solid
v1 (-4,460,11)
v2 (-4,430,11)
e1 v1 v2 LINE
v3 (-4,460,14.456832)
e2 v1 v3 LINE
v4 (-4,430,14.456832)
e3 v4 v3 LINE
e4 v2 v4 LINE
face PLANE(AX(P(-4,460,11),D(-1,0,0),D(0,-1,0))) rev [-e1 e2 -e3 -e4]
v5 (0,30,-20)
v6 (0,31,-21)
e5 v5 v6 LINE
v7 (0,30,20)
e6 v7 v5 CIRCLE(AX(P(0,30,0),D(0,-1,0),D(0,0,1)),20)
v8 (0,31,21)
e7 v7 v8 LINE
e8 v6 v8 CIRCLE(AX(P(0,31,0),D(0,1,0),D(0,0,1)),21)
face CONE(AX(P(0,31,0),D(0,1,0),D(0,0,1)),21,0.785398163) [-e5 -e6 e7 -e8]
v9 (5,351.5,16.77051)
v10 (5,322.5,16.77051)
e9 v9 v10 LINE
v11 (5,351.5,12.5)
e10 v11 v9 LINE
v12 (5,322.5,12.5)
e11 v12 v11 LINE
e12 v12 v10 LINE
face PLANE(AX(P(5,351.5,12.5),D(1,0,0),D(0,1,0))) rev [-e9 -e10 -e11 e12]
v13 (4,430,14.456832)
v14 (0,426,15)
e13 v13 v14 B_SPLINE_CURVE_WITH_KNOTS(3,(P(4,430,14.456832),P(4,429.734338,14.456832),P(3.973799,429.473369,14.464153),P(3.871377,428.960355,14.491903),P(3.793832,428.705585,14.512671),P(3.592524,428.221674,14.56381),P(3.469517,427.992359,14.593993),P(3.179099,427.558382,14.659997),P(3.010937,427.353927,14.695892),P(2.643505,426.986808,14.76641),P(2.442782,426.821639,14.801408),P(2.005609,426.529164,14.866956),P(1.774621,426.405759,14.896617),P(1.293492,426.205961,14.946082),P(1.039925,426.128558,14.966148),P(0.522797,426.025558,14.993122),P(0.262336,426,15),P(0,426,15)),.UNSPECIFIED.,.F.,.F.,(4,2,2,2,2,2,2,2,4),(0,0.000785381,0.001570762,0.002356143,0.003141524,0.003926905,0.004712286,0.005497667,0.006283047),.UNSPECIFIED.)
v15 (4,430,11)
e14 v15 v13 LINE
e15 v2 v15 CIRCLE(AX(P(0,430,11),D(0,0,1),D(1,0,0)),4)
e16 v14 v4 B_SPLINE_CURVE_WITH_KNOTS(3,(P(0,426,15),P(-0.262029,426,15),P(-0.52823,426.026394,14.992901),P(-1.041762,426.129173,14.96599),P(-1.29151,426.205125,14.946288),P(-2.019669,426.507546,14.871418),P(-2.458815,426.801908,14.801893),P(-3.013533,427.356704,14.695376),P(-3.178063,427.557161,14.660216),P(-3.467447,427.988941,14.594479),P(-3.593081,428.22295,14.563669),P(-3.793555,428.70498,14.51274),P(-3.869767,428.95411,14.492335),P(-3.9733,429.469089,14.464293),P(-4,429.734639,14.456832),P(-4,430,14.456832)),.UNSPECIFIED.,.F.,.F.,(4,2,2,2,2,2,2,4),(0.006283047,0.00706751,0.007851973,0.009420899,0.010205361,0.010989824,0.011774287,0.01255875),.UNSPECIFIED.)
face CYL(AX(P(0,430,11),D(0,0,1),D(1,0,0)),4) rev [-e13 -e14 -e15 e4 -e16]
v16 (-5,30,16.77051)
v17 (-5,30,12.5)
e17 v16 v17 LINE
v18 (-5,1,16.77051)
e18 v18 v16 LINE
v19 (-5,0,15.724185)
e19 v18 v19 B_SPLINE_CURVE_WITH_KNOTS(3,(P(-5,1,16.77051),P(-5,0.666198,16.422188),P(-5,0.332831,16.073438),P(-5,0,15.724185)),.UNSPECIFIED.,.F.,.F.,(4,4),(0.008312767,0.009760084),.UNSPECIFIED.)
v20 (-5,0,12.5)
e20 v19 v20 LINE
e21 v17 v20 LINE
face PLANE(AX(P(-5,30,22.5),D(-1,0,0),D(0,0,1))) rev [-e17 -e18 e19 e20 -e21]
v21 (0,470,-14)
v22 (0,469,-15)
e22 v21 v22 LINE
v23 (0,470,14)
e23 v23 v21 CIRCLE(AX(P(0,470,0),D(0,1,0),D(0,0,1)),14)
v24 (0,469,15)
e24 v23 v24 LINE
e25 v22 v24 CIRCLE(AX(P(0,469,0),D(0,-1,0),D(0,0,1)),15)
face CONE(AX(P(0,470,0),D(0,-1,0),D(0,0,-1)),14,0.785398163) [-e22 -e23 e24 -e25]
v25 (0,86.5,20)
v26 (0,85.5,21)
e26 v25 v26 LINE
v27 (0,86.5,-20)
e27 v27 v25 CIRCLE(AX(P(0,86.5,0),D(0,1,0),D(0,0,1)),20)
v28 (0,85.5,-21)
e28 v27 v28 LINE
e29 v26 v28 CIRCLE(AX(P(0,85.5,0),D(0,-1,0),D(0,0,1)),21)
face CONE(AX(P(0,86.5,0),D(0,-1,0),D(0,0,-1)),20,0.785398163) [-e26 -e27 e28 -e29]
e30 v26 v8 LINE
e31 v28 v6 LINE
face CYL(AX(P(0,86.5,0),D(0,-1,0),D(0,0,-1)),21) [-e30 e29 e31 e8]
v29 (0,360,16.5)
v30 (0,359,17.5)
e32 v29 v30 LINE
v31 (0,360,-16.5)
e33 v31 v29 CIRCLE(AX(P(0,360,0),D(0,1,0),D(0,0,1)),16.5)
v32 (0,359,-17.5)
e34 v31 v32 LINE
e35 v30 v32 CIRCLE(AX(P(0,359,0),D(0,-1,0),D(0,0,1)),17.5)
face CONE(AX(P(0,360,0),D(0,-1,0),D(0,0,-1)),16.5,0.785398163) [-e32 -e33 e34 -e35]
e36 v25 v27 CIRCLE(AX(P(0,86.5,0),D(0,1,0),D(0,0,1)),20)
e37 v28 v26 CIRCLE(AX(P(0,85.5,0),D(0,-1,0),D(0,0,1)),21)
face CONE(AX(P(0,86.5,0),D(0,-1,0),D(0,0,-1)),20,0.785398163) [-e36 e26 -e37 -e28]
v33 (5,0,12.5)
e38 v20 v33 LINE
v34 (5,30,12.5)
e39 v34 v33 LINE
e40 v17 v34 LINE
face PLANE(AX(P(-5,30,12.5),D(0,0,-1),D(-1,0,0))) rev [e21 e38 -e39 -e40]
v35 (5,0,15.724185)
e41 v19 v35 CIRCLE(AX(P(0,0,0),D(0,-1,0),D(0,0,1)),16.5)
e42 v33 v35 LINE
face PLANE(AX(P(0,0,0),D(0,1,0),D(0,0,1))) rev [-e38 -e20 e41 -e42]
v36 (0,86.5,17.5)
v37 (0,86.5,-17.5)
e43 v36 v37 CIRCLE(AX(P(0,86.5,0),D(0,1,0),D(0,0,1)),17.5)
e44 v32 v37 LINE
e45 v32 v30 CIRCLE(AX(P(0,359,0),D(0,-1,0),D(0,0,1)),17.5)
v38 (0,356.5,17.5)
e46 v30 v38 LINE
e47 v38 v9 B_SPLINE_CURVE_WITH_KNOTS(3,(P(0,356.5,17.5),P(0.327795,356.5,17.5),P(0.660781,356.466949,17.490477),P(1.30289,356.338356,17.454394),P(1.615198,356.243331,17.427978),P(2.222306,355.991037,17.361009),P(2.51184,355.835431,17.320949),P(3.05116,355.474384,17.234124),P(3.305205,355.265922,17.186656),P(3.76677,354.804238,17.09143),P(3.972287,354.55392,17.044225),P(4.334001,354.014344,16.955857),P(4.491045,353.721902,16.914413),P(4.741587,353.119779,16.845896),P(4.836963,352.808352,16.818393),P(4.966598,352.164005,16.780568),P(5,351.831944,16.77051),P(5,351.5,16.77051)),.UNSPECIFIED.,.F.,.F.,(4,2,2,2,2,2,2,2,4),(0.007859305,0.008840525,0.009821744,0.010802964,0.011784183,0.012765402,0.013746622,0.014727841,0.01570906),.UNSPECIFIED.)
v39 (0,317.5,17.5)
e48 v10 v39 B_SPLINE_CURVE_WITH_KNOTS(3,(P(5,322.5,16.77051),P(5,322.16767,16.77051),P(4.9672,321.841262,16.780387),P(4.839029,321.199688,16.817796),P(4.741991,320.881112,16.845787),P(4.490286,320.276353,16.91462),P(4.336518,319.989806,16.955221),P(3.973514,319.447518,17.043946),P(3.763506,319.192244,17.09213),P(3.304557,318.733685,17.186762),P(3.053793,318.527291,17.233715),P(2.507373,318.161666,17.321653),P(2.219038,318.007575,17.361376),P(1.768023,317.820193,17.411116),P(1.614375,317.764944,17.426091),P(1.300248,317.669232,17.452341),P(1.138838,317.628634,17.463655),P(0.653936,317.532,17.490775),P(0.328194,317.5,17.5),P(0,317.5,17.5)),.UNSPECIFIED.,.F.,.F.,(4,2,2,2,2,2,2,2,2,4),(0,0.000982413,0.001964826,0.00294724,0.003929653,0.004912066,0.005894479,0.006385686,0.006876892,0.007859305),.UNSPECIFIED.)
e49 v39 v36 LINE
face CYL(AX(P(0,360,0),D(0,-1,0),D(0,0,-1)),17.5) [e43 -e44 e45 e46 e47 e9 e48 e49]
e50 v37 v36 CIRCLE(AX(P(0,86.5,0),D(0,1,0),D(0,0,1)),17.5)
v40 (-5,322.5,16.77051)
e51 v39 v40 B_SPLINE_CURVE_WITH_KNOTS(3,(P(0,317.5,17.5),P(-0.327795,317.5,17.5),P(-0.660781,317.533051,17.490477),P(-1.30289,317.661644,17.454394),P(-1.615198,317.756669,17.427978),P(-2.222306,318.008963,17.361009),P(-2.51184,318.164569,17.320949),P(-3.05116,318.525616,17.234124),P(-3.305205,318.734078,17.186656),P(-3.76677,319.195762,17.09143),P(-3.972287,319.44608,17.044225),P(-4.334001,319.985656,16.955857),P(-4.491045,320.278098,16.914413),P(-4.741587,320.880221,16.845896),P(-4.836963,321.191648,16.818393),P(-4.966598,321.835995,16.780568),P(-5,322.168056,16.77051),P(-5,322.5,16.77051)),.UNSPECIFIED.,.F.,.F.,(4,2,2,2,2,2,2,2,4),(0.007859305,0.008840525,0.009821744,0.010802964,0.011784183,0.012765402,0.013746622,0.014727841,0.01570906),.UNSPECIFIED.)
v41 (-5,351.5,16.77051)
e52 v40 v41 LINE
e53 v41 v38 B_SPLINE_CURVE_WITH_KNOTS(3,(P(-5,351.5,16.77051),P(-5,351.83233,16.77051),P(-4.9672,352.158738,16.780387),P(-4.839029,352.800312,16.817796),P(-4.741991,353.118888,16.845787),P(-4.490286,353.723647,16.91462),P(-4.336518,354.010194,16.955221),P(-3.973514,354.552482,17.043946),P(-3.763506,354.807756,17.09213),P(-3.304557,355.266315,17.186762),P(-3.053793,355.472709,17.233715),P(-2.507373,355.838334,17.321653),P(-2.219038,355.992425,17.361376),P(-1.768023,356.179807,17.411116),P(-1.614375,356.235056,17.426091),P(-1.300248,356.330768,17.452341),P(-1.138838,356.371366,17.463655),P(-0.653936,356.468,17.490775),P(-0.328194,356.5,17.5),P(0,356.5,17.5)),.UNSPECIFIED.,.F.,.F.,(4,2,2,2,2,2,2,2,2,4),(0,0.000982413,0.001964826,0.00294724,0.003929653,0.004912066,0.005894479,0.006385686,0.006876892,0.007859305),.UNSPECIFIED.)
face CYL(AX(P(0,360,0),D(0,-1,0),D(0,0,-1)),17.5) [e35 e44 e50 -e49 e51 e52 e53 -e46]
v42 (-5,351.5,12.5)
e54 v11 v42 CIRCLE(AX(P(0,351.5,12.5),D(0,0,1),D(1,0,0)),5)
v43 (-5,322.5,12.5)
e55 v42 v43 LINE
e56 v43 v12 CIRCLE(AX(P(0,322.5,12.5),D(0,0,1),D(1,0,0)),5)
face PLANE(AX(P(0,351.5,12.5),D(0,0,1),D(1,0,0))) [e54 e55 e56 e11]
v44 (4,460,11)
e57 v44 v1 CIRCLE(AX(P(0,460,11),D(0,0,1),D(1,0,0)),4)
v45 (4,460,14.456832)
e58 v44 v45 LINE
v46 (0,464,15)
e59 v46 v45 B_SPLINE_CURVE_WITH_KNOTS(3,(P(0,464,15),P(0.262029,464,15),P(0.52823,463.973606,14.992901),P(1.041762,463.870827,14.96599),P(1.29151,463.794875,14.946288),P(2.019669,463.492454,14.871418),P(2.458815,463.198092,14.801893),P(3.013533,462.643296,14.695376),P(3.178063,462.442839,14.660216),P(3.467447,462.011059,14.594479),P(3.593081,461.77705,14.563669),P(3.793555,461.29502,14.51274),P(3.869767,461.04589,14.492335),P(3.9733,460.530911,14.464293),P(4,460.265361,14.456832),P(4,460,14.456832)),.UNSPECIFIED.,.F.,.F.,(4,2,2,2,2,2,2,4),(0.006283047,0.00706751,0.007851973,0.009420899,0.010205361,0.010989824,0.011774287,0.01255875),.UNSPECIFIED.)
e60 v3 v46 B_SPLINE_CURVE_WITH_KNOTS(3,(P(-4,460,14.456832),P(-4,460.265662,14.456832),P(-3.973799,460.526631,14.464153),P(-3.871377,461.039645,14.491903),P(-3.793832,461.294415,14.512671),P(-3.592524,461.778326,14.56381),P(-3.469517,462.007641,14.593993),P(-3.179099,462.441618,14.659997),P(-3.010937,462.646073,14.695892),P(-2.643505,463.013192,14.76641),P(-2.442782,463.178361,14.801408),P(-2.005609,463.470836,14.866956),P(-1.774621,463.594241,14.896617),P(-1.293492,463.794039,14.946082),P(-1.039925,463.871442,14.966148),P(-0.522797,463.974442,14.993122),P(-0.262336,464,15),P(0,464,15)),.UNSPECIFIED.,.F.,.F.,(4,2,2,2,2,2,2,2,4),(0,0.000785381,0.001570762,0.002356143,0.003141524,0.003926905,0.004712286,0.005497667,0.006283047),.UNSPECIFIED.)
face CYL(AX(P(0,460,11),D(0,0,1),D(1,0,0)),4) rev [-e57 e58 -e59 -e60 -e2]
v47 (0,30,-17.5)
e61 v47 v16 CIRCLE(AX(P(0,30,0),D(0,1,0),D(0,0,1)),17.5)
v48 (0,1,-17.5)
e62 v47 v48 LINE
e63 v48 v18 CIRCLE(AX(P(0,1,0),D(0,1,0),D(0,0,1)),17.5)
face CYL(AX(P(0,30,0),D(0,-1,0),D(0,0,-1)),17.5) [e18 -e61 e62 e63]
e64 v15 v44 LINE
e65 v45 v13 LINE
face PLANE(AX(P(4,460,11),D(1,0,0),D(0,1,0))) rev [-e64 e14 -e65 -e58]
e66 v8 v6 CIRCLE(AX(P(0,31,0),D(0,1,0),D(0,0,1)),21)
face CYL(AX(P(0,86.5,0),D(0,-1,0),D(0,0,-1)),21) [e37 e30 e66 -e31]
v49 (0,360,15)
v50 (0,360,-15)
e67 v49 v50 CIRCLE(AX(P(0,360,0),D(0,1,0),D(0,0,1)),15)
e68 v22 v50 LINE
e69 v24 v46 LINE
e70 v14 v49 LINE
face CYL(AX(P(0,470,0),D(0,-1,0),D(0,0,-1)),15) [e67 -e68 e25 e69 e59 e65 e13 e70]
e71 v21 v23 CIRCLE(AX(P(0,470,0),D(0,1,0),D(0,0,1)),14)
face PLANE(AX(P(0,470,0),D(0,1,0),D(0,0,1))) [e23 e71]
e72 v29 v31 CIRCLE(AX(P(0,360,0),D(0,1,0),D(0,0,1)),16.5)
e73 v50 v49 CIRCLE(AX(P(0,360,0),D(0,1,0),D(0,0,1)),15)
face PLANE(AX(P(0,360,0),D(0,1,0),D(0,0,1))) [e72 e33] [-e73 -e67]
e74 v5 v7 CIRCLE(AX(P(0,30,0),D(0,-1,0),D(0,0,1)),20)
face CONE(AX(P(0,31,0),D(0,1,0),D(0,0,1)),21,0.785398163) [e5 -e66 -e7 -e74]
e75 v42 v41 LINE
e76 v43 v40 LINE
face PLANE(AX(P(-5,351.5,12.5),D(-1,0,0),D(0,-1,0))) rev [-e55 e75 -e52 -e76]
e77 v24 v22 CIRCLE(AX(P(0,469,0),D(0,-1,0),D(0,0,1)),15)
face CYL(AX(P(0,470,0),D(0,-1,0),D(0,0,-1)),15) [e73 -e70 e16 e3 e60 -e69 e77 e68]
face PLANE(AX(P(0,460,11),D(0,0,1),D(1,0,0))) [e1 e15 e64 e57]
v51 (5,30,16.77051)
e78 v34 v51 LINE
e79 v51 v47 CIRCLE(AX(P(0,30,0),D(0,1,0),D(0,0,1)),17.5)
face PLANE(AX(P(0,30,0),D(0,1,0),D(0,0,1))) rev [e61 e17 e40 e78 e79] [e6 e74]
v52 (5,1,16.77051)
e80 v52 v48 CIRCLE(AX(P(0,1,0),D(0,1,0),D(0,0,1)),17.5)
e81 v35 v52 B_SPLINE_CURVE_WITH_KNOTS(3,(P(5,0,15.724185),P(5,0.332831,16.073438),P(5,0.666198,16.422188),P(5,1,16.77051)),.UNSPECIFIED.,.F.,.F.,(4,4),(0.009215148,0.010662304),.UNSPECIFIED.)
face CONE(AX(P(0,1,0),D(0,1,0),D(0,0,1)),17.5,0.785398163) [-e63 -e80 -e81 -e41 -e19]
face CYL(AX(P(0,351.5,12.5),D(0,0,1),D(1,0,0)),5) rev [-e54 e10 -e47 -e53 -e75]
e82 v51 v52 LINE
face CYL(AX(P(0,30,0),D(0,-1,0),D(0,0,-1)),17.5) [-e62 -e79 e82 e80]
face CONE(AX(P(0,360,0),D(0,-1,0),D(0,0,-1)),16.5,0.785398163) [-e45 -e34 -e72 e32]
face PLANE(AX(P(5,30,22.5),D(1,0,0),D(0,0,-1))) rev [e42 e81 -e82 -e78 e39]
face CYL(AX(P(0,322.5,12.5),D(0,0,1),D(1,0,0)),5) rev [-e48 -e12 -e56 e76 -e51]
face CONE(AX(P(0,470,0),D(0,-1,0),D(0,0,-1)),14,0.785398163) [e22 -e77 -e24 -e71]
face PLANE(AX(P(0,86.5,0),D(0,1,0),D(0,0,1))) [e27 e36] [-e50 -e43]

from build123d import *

# Parameters (mm, degrees)
SKETCH1_R           = 17.5
BOSS_EXTRUDE1_DEPTH = 30
SKETCH2_R           = 21
BOSS_EXTRUDE2_DEPTH = 56.5
SKETCH3_R           = 17.5
BOSS_EXTRUDE3_DEPTH = 273.5
SKETCH4_R           = 15
BOSS_EXTRUDE4_DEPTH = 110
CHAMFER1_SIZE       = 1
CHAMFER3_SIZE       = 1
SKETCH5_W           = 10
SKETCH5_H           = 10
CUT_EXTRUDE1_DEPTH  = 30
CUT_EXTRUDE10_DEPTH = 5.5
CUT_EXTRUDE11_DEPTH = 7


with BuildPart() as part:
    # Sketch1 → Boss-Extrude1 (new body)
    with BuildSketch(Plane(origin=(0, 0, 0), x_dir=(1, 0, 0), z_dir=(0, 1, 0))):
        with Locations(Location((0, 0, 0), (0, 0, 270))):
            Circle(SKETCH1_R)
    extrude(amount=BOSS_EXTRUDE1_DEPTH)

    # Sketch2 → Boss-Extrude2 (add)
    with BuildSketch(Plane(origin=(0, 30, 0), x_dir=(1, 0, 0), z_dir=(0, 1, 0))):
        with Locations(Location((0, 0, 0), (0, 0, 270))):
            Circle(SKETCH2_R)
    extrude(amount=BOSS_EXTRUDE2_DEPTH)

    # Sketch3 → Boss-Extrude3 (add)
    with BuildSketch(Plane(origin=(0, 86.5, 0), x_dir=(1, 0, 0), z_dir=(0, 1, 0))):
        with Locations(Location((0, 0, 0), (0, 0, 270))):
            Circle(SKETCH3_R)
    extrude(amount=BOSS_EXTRUDE3_DEPTH)

    # Sketch4 → Boss-Extrude4 (add)
    with BuildSketch(Plane(origin=(0, 360, 0), x_dir=(1, 0, 0), z_dir=(0, 1, 0))):
        with Locations(Location((0, 0, 0), (0, 0, 270))):
            Circle(SKETCH4_R)
    extrude(amount=BOSS_EXTRUDE4_DEPTH)

    # Chamfer1
    chamfer1_edges = [part.edges().sort_by_distance(p)[0] for p in [
        (0, 0, -17.5),
    ]]
    chamfer(chamfer1_edges, length=CHAMFER1_SIZE)

    # Chamfer3
    chamfer3_edges = [part.edges().sort_by_distance(p)[0] for p in [
        (0, 360, -17.5),
        (0, 470, -15),
        (0, 30, -21),
        (0, 86.5, -21),
    ]]
    chamfer(chamfer3_edges, length=CHAMFER3_SIZE)

    # Sketch5 → Cut-Extrude1 (cut)
    with BuildSketch(Plane.XZ):
        with Locations((0, 17.5)):
            Rectangle(SKETCH5_W, SKETCH5_H)
    extrude(amount=-CUT_EXTRUDE1_DEPTH, mode=Mode.SUBTRACT)

    # Sketch8 → Cut-Extrude10 (cut)
    with BuildSketch(Plane.XY.offset(18)):
        with BuildLine():
            Line((5, 351.5), (5, 322.5))
            ThreePointArc((5, 322.5), (0, 317.5), (-5, 322.5))
            Line((-5, 322.5), (-5, 351.5))
            ThreePointArc((-5, 351.5), (0, 356.5), (5, 351.5))
        make_face()
    extrude(amount=-CUT_EXTRUDE10_DEPTH, mode=Mode.SUBTRACT)

    # Sketch9 → Cut-Extrude11 (cut)
    with BuildSketch(Plane.XY.offset(18)):
        with BuildLine():
            Line((4, 460), (4, 430))
            ThreePointArc((4, 430), (0, 426), (-4, 430))
            Line((-4, 430), (-4, 460))
            ThreePointArc((-4, 460), (0, 464), (4, 460))
        make_face()
    extrude(amount=-CUT_EXTRUDE11_DEPTH, mode=Mode.SUBTRACT)


solid = part.part
